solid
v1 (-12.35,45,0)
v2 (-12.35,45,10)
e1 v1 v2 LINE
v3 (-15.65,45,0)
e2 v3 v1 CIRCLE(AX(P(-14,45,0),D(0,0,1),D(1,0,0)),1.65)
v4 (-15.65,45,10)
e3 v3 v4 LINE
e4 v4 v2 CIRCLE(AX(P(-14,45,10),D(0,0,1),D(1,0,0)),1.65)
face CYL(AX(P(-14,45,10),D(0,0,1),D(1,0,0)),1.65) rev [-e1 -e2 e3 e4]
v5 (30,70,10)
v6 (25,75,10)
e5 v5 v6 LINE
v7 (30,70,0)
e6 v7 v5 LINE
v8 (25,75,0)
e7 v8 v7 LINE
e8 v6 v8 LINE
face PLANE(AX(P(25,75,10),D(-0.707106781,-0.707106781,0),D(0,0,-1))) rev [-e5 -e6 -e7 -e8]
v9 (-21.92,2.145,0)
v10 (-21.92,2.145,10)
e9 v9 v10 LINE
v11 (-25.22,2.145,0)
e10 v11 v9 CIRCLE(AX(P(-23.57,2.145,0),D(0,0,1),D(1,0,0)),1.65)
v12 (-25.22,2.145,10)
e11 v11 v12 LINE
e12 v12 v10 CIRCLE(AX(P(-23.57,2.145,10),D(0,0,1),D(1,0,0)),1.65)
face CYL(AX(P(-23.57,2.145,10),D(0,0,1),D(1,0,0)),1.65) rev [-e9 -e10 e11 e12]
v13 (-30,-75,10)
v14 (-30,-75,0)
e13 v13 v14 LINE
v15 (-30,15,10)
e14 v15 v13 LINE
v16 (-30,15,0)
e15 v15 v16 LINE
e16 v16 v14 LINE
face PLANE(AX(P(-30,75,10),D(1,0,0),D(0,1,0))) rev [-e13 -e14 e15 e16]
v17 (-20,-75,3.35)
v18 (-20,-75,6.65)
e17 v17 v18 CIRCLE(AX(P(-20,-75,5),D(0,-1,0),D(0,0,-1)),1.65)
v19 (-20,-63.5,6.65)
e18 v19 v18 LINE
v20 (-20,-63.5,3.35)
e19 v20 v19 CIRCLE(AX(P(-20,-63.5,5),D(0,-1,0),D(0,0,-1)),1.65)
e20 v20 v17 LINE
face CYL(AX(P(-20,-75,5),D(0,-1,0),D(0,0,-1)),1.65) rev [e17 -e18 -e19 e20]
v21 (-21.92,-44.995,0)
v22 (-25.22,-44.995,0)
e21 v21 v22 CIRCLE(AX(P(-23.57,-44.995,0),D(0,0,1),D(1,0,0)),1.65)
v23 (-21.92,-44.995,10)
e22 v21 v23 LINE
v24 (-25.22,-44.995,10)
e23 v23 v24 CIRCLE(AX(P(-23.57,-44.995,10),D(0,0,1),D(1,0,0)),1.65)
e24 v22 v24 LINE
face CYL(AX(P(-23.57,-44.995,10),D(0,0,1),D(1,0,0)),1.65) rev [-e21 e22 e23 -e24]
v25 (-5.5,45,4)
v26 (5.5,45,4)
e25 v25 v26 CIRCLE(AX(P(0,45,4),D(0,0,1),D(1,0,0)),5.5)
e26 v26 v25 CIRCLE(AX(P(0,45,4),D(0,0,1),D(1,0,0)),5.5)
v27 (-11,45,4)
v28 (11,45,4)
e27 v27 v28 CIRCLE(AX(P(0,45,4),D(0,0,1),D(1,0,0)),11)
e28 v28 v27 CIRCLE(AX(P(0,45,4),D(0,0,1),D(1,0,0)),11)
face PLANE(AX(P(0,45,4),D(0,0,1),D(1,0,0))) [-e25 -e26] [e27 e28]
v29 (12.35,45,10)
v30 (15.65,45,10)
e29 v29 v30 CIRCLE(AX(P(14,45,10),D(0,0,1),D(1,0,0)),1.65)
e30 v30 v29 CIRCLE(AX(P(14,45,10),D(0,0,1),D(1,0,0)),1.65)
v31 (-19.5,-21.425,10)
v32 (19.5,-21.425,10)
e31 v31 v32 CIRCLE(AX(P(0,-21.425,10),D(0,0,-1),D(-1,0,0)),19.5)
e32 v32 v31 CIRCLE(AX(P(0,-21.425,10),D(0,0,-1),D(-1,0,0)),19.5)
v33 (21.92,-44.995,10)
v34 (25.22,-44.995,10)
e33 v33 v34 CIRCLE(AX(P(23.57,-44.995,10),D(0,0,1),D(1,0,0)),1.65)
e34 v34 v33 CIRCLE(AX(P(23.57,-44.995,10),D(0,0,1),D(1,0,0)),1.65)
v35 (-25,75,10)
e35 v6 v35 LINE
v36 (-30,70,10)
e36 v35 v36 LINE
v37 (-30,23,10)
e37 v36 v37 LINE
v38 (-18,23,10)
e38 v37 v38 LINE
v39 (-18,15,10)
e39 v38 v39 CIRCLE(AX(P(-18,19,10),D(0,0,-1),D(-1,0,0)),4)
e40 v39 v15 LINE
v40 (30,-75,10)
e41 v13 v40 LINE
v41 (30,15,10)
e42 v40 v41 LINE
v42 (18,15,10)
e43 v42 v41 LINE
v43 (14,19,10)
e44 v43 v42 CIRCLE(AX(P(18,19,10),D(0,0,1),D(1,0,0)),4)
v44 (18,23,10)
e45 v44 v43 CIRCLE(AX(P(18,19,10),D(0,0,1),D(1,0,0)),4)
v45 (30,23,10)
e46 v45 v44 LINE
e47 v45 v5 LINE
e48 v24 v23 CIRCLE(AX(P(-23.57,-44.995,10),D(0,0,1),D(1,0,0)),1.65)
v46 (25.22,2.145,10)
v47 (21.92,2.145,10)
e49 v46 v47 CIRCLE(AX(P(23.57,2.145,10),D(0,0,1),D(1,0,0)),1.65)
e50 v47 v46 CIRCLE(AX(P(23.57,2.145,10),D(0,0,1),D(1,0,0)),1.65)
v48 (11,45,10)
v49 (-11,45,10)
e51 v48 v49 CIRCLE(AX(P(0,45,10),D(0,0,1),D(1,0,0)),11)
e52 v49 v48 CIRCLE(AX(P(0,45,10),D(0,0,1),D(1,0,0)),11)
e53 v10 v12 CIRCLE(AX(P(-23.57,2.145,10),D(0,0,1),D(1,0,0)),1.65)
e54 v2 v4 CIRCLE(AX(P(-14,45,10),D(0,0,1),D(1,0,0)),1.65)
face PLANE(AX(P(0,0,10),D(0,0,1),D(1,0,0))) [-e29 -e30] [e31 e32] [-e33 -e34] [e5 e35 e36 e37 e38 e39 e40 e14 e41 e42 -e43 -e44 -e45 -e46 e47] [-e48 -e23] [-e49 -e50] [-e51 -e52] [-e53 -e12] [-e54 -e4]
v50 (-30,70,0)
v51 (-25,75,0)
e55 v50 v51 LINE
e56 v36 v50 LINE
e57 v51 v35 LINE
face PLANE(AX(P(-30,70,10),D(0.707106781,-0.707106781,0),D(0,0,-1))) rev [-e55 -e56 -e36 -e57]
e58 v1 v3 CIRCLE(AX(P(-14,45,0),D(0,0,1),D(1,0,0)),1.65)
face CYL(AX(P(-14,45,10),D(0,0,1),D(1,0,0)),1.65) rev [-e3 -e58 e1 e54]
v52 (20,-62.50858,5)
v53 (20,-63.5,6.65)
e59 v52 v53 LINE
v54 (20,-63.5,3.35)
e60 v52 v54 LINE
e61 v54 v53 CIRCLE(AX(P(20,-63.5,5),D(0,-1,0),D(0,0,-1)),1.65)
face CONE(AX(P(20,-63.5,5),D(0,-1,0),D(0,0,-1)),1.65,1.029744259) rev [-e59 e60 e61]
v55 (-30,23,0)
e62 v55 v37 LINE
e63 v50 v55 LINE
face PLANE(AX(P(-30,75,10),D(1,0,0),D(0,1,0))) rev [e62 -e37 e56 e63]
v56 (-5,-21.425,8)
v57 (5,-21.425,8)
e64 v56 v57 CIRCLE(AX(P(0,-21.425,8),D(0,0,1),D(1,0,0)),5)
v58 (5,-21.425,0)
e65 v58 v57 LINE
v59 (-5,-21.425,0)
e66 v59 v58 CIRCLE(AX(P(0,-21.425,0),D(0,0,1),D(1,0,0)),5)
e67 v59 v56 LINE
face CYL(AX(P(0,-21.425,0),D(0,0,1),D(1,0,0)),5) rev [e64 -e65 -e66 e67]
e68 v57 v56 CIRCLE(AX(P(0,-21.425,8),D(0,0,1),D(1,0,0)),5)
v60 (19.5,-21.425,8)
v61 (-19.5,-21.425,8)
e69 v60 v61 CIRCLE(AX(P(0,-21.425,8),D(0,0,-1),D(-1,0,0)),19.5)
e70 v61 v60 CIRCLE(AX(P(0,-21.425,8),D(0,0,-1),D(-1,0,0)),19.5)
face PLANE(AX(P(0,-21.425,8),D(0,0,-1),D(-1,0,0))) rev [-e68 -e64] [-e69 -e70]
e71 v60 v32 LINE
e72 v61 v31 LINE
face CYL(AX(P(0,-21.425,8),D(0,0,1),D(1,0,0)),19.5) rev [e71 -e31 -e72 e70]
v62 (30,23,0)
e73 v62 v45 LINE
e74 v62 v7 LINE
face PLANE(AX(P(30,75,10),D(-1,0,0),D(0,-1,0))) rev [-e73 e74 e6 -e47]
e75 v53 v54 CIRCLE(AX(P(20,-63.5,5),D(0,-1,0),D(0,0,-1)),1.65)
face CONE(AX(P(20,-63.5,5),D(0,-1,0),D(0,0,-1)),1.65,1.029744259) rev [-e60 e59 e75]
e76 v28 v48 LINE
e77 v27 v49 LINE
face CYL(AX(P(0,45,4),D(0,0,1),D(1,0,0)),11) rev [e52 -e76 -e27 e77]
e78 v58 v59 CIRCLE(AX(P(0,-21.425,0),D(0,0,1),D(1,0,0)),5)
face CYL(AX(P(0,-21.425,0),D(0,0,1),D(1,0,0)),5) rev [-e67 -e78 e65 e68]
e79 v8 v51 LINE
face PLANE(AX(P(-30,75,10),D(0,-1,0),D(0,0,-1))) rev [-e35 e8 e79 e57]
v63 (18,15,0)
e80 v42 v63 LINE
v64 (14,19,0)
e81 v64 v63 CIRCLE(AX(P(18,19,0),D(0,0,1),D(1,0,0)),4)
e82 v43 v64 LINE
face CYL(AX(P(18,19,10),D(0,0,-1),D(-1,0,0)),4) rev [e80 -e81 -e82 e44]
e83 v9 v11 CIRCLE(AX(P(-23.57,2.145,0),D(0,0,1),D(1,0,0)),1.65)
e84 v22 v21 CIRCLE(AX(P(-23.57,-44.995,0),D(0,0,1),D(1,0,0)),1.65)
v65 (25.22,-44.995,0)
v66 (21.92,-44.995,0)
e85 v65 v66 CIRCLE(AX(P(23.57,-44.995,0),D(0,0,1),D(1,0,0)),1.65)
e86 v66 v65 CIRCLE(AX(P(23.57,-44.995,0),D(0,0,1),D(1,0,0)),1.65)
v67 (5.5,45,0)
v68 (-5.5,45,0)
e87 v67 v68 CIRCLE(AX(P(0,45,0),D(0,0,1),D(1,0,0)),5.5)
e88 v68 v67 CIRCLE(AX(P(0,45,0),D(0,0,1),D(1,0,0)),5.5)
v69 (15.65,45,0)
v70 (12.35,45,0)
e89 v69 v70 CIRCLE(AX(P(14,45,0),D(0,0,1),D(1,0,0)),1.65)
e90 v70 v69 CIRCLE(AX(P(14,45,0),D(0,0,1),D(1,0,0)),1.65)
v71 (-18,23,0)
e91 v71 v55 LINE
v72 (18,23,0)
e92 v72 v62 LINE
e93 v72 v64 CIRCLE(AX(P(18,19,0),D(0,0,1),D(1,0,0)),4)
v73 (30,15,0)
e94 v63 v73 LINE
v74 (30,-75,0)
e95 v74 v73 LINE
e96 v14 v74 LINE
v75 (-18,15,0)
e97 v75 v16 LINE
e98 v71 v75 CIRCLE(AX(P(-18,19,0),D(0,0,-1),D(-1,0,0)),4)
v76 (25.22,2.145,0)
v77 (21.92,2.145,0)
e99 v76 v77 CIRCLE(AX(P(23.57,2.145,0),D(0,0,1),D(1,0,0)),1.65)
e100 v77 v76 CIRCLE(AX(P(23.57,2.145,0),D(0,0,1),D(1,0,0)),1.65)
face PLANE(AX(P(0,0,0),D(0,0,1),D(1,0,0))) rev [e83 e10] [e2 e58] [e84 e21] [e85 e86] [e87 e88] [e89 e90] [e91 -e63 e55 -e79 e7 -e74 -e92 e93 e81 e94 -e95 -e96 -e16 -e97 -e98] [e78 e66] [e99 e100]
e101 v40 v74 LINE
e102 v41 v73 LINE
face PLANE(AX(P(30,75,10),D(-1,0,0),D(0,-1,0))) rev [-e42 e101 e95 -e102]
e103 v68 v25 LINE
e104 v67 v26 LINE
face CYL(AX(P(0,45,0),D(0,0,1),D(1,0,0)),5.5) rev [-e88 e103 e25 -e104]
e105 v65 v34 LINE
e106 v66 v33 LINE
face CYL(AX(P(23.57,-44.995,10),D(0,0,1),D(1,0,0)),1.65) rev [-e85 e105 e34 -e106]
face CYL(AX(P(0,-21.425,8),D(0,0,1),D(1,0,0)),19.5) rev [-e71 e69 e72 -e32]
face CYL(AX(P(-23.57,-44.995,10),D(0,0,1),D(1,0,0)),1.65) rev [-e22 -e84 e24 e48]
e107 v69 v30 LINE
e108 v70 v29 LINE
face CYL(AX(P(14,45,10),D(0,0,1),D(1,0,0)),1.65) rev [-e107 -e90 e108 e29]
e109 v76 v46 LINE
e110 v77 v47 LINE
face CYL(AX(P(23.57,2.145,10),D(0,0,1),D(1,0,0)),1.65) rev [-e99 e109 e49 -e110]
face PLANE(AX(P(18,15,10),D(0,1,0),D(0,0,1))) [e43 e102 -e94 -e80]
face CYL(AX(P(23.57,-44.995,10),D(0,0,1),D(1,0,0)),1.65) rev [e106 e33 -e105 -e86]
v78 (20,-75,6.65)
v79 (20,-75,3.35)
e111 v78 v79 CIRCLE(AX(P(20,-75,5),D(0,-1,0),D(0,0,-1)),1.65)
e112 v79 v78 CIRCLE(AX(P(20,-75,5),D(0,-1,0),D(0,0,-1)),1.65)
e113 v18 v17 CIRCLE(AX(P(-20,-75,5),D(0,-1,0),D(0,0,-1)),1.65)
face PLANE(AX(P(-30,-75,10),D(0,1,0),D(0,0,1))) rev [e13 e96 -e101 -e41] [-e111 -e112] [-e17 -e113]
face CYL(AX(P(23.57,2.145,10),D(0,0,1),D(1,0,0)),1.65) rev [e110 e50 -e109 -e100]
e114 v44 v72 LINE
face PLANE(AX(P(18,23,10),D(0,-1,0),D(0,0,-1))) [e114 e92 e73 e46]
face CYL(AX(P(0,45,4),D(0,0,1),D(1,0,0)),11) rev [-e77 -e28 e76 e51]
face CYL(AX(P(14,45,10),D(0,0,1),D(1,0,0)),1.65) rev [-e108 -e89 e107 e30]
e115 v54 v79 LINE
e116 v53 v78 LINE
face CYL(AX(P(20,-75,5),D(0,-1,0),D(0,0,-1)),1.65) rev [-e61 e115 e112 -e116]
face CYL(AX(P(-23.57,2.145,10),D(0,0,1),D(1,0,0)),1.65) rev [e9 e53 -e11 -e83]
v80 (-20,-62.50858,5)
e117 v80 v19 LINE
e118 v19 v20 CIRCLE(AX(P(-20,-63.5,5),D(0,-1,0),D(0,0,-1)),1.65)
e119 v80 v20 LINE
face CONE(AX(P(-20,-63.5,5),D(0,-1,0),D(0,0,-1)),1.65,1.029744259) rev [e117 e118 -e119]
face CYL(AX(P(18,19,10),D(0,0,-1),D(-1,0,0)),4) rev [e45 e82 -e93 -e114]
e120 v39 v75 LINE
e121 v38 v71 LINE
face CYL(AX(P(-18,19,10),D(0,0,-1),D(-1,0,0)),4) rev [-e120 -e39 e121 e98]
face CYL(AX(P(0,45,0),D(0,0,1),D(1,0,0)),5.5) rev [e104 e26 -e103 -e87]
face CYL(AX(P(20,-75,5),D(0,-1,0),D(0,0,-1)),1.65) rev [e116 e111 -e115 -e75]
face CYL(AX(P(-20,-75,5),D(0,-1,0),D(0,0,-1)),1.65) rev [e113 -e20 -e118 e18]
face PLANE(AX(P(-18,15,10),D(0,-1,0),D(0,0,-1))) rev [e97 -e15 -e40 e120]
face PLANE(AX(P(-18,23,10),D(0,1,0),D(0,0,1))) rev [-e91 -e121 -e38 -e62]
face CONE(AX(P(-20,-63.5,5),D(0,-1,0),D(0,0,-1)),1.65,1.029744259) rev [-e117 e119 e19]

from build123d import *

# Parameters (mm, degrees)
SKETCH1_W             = 60
SKETCH1_H             = 150
BOSS_EXTRUDE1_DEPTH   = 10
CHAMFER1_SIZE         = 5
CUT_EXTRUDE5_START    = -10
SKETCH5_R             = 19.5
CUT_EXTRUDE5_DEPTH    = 2
SKETCH6_R             = 5
CUT_EXTRUDE6_DEPTH    = 82.172655494
M4_TAPPED_HOLE1_D     = 3.3
SKETCH9_R             = 11
CUT_EXTRUDE7_DEPTH    = 6
SKETCH10_R            = 5.5
CUT_EXTRUDE8_DEPTH    = 82
CUT_EXTRUDE9_DEPTH    = 82.39410298
M4_TAPPED_HOLE2_D     = 3.3
M4_TAPPED_HOLE3_D     = 3.3
M4_TAPPED_HOLE3_DEPTH = 11.5
M4_TAPPED_HOLE3_TIP   = 0.991420021


with BuildPart() as part:
    # Sketch1 → Boss-Extrude1 (new body)
    with BuildSketch(Plane.XY):
        Rectangle(SKETCH1_W, SKETCH1_H)
    extrude(amount=BOSS_EXTRUDE1_DEPTH)

    # Chamfer1
    chamfer1_edges = [part.edges().sort_by_distance(p)[0] for p in [
        (-30, 75, 5),
        (30, 75, 5),
    ]]
    chamfer(chamfer1_edges, length=CHAMFER1_SIZE)

    # Sketch5 → Cut-Extrude5 (cut)
    with BuildSketch(Plane(origin=(0, 0, 0), x_dir=(-1, 0, 0), z_dir=(0, 0, -1)).offset(CUT_EXTRUDE5_START)):
        with Locations((0, -21.425)):
            Circle(SKETCH5_R)
    extrude(amount=CUT_EXTRUDE5_DEPTH, mode=Mode.SUBTRACT)

    # Sketch6 → Cut-Extrude6 (cut, through all)
    with BuildSketch(Plane.XY.offset(8)):
        with Locations((0, -21.425)):
            Circle(SKETCH6_R)
    extrude(amount=-CUT_EXTRUDE6_DEPTH, mode=Mode.SUBTRACT)

    # M4 Tapped Hole1 (through all)
    with Locations(Plane.XY.offset(10)):
        with Locations((-23.57, 2.145), (-23.57, -44.995), (23.57, 2.145), (23.57, -44.995)):
            Hole(M4_TAPPED_HOLE1_D / 2)

    # Sketch9 → Cut-Extrude7 (cut)
    with BuildSketch(Plane.XY.offset(10)):
        with Locations((0, 45)):
            Circle(SKETCH9_R)
    extrude(amount=-CUT_EXTRUDE7_DEPTH, mode=Mode.SUBTRACT)

    # Sketch10 → Cut-Extrude8 (cut, through all)
    with BuildSketch(Plane.XY.offset(4)):
        with Locations((0, 45)):
            Circle(SKETCH10_R)
    extrude(amount=-CUT_EXTRUDE8_DEPTH, mode=Mode.SUBTRACT)

    # Sketch11 → Cut-Extrude9 (cut, through all)
    with BuildSketch(Plane(origin=(0, 0, 0), x_dir=(-1, 0, 0), z_dir=(0, 0, -1))):
        with BuildLine():
            Line((18, 23), (40.992730917, 23))
            ThreePointArc((40.992730917, 23), (44.992730917, 19), (40.992730917, 15))
            Line((40.992730917, 15), (18, 15))
            ThreePointArc((18, 15), (14, 19), (18, 23))
        make_face()
    cut_extrude9 = extrude(amount=-CUT_EXTRUDE9_DEPTH, mode=Mode.SUBTRACT)

    # Mirror1: Cut-Extrude9 across plane
    add(cut_extrude9.mirror(Plane(origin=(0, 0, 0), x_dir=(0, 0, 1), z_dir=(1, 0, 0))), mode=Mode.SUBTRACT)

    # M4 Tapped Hole2 (through all)
    with Locations(Plane.XY.offset(10)):
        with Locations((-14, 45), (14, 45)):
            Hole(M4_TAPPED_HOLE2_D / 2)

    # M4 Tapped Hole3
    with Locations(Plane(origin=(0, -75, 0), x_dir=(-1, 0, 0), z_dir=(0, -1, 0))):
        with Locations((20, -5), (-20, -5)):
            Hole(M4_TAPPED_HOLE3_D / 2, depth=M4_TAPPED_HOLE3_DEPTH)
            with Locations((0, 0, -(M4_TAPPED_HOLE3_DEPTH + M4_TAPPED_HOLE3_TIP / 2))):  # 118° drill point
                Cone(0, M4_TAPPED_HOLE3_D / 2, M4_TAPPED_HOLE3_TIP, mode=Mode.SUBTRACT)


solid = part.part
